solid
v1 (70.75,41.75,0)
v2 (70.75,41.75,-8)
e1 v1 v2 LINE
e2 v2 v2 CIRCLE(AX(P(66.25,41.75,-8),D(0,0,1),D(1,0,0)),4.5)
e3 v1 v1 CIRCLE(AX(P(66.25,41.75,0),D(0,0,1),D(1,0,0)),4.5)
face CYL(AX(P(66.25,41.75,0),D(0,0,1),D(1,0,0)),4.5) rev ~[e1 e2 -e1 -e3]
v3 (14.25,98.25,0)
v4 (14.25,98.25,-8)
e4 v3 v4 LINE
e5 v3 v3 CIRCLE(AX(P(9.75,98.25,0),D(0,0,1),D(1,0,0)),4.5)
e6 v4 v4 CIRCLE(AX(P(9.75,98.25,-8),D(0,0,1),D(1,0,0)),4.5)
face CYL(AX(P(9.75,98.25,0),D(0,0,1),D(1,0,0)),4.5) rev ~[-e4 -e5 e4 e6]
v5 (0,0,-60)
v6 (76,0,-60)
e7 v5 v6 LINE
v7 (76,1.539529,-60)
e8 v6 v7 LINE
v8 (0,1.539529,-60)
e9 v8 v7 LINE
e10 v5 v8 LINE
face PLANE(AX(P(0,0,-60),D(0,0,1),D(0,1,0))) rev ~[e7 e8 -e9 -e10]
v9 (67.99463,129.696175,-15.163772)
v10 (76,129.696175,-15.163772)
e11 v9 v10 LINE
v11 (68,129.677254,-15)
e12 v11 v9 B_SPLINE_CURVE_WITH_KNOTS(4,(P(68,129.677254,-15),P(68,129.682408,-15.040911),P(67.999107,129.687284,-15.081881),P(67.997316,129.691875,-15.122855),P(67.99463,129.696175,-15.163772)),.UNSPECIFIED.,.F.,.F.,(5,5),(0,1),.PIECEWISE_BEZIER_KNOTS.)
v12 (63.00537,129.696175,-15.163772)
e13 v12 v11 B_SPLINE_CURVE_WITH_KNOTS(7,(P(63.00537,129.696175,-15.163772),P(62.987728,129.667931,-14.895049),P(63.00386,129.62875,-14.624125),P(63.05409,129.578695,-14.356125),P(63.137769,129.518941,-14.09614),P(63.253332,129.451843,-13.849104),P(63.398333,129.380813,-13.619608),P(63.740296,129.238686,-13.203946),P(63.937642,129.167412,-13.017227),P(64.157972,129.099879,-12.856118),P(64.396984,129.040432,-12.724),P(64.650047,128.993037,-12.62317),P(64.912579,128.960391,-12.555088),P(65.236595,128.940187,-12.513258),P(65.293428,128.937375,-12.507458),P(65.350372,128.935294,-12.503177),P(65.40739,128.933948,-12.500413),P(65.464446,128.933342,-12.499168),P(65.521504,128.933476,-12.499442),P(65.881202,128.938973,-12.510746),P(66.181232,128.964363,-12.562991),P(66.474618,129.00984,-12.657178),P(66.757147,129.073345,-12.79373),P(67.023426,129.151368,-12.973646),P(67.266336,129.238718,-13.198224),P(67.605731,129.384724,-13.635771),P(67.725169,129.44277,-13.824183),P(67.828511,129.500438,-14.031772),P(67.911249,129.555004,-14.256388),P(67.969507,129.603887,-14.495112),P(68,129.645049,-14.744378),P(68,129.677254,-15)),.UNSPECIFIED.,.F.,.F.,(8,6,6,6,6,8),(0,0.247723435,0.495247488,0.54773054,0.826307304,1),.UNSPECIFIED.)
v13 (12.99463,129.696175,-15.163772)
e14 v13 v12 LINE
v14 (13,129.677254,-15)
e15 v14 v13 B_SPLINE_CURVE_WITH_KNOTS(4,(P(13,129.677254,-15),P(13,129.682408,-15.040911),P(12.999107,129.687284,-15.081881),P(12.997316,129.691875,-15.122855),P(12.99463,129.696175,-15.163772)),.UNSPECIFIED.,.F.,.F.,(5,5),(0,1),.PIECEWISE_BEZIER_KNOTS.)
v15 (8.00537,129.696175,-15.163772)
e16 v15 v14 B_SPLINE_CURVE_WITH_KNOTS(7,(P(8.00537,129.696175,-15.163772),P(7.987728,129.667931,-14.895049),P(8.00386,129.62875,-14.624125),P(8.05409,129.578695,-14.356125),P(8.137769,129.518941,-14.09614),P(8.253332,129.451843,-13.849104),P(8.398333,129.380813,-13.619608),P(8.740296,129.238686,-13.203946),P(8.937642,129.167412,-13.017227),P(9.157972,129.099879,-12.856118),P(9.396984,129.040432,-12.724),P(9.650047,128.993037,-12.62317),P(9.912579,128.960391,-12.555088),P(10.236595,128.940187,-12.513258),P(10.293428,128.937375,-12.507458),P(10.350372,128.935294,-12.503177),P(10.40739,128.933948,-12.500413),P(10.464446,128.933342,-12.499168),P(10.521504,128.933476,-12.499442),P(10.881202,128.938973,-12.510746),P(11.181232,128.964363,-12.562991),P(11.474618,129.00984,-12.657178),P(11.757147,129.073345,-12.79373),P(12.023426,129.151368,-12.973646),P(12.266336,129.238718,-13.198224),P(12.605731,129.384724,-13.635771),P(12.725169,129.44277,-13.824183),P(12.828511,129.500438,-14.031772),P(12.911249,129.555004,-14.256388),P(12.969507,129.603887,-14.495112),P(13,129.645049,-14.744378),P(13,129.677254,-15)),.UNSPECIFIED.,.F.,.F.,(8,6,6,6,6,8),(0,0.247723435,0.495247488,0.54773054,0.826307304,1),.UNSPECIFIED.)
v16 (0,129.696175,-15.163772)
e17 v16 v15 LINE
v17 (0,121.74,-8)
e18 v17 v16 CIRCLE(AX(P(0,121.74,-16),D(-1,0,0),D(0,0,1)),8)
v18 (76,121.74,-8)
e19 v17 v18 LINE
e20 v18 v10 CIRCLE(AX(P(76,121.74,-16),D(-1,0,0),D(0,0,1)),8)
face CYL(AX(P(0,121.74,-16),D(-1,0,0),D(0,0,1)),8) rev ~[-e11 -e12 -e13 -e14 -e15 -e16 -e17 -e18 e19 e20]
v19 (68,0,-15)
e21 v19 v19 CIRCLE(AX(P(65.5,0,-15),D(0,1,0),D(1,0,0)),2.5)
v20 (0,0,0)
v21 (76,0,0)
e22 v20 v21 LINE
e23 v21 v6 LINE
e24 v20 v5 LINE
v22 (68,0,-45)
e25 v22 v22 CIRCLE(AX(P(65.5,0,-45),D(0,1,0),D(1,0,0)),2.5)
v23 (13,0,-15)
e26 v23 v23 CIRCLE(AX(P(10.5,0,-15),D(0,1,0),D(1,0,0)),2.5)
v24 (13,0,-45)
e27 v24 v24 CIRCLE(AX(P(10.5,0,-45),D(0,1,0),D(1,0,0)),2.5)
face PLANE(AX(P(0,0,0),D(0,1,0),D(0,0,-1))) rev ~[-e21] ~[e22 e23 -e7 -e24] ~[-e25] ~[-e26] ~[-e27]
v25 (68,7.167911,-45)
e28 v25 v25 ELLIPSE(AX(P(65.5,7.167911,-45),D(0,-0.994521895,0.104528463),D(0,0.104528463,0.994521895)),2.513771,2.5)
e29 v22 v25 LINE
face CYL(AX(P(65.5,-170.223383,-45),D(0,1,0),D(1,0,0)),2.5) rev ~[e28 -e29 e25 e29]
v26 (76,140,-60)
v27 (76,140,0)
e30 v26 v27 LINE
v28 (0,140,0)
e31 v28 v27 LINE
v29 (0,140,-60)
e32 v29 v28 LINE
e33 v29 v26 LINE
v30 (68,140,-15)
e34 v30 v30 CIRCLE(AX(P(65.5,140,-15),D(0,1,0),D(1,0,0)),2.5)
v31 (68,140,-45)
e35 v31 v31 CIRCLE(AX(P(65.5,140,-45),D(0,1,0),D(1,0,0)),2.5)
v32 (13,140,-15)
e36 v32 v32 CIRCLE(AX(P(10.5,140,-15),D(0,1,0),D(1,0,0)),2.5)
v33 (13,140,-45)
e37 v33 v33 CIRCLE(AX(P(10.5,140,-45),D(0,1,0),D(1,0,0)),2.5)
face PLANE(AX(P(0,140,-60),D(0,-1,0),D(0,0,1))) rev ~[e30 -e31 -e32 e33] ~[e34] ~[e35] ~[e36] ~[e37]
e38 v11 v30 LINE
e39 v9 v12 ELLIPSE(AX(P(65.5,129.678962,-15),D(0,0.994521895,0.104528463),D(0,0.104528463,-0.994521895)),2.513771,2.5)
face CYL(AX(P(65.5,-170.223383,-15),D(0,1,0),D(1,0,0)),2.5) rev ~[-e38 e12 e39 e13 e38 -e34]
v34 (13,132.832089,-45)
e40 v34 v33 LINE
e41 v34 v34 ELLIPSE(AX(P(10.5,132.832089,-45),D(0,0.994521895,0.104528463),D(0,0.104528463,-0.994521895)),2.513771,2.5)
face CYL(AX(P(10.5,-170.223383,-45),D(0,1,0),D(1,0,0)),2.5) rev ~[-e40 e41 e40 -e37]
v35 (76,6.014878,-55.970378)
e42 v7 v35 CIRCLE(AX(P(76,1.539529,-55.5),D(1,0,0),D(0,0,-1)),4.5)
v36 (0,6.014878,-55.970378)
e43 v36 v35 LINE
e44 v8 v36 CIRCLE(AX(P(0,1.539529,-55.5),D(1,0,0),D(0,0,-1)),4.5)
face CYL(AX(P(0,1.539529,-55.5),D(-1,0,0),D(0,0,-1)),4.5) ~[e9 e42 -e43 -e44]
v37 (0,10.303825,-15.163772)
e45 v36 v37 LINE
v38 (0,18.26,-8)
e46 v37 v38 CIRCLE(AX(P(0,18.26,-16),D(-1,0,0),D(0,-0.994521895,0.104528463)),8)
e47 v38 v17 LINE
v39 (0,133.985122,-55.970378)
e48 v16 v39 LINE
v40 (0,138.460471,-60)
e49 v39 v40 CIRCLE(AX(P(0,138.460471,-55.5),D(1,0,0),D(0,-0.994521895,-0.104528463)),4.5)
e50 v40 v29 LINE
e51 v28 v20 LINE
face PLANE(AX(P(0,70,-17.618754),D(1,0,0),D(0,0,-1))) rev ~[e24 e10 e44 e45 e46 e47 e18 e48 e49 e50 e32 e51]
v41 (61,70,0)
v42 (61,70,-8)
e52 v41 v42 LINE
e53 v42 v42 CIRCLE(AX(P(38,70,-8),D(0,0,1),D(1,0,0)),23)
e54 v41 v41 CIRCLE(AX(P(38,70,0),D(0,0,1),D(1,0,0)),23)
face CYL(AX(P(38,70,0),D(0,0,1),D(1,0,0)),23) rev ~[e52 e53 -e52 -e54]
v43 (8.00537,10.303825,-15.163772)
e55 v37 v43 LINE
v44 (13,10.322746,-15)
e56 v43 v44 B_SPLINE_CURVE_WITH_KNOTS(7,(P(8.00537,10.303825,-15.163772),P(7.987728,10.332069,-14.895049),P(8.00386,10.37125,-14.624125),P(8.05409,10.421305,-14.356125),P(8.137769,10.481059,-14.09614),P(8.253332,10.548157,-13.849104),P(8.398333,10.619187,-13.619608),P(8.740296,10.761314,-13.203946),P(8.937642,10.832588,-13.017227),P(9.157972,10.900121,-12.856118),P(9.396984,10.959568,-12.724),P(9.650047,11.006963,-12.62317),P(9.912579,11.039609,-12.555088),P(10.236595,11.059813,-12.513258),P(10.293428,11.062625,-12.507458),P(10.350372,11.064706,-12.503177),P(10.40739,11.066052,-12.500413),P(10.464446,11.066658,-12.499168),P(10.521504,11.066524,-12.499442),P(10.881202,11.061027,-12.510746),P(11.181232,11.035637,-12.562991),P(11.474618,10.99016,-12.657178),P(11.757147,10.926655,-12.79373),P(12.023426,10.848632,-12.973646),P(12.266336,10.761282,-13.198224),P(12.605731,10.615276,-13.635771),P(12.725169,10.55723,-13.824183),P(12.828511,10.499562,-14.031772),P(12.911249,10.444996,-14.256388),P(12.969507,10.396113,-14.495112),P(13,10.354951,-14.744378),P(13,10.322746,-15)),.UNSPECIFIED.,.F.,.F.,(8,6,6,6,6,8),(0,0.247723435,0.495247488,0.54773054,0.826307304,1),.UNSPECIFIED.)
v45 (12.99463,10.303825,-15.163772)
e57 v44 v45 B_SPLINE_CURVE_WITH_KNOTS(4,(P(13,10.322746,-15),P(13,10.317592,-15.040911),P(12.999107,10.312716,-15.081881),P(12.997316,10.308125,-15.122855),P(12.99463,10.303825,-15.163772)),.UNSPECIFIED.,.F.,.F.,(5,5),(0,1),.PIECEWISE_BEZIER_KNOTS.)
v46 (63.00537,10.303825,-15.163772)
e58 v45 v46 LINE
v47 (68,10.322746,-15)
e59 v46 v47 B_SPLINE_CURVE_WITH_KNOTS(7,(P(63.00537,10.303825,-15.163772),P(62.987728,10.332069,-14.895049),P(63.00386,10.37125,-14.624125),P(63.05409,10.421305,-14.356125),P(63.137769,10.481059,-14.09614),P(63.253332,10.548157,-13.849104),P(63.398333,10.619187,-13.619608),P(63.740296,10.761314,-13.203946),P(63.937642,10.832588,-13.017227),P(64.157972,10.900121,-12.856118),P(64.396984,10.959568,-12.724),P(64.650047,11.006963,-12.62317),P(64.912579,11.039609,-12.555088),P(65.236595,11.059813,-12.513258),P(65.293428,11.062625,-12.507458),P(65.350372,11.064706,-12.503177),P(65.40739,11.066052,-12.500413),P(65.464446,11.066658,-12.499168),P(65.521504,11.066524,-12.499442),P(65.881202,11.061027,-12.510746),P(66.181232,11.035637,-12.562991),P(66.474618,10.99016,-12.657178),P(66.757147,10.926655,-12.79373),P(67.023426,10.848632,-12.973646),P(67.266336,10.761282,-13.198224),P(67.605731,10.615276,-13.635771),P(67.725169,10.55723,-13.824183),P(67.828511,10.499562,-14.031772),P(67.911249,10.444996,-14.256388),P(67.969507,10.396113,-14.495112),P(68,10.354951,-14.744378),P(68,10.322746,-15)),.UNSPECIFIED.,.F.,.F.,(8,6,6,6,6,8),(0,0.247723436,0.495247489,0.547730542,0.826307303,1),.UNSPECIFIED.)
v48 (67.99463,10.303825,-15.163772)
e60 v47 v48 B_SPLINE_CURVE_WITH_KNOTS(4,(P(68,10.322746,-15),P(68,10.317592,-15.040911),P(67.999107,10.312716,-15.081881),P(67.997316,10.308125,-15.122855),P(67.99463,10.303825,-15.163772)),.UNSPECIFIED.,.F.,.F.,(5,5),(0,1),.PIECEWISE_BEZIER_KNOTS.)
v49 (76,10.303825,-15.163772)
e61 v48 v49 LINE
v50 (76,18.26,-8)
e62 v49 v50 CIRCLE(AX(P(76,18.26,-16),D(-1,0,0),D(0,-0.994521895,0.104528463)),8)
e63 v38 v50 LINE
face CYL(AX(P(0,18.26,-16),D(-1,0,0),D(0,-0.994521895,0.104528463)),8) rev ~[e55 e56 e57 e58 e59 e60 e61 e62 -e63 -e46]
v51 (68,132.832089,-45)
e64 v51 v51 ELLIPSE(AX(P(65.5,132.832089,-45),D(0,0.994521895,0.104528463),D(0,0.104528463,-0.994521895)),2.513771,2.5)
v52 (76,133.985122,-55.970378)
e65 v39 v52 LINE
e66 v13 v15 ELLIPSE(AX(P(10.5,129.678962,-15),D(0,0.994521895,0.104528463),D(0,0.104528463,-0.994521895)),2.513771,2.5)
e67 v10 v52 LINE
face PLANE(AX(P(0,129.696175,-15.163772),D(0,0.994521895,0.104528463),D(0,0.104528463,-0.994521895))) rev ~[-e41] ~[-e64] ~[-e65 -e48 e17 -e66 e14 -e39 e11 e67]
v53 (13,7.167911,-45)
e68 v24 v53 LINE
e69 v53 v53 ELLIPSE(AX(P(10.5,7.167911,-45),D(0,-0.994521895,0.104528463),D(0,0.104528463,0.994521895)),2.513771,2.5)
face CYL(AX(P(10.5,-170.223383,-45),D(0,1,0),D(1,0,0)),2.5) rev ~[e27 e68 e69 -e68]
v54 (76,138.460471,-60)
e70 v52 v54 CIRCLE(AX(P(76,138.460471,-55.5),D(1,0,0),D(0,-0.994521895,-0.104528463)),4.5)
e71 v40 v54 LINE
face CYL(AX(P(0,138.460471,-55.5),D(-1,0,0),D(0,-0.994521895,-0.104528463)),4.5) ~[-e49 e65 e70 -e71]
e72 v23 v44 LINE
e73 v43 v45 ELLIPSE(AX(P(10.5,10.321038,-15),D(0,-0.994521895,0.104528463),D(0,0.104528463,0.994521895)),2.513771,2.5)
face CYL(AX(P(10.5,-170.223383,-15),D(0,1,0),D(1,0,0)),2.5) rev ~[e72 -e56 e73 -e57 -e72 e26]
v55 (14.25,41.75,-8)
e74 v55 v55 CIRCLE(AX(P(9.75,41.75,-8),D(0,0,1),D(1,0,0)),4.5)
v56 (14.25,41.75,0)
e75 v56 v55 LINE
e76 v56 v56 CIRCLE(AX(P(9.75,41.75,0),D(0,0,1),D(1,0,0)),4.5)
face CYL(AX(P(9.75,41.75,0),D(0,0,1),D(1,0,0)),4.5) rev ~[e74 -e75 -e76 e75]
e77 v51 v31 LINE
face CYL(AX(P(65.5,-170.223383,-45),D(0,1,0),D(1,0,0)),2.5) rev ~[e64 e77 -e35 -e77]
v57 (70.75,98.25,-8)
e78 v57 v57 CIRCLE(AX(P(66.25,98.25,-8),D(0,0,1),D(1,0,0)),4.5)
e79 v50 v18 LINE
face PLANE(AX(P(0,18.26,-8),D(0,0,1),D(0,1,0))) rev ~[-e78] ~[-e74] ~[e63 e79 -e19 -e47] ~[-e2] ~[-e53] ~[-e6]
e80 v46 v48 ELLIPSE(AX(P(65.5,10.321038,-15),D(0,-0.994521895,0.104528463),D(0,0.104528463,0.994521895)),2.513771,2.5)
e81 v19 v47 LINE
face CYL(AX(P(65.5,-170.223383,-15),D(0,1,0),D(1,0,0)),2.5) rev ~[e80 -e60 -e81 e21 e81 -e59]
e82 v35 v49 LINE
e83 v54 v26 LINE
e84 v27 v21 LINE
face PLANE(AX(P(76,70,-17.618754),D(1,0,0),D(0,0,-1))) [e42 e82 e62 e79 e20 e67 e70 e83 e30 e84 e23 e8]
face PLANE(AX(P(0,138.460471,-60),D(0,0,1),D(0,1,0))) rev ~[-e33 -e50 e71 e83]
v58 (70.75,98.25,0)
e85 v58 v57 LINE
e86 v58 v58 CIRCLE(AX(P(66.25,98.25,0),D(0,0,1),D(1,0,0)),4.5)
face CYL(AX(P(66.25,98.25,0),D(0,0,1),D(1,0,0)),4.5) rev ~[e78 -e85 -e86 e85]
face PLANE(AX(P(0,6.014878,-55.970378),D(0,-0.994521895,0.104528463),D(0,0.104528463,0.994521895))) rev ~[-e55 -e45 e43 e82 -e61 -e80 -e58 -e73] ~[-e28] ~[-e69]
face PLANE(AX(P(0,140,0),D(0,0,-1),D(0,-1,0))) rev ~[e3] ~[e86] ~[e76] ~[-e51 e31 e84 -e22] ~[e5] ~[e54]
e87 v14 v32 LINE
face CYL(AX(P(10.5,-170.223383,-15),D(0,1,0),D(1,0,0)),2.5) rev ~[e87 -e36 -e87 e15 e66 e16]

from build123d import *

# Parameters (mm, degrees)
MEMBER_1_DEPTH      = 76
SKETCH_4_R          = 23
CUT_EXTRUDE_1_DEPTH = 171.223382648
SKETCH_6_R          = 4.5
CUT_EXTRUDE_2_DEPTH = 171.223382648
HOLE_WIZARD_M6_1_D  = 5


with BuildPart() as part:
    # Sketch11 → Member 1 (new body)
    with BuildSketch(Plane(origin=(0, 0, 0), x_dir=(0, 0, -1), z_dir=(1, 0, 0))):
        with BuildLine():
            Line((60, 140), (0, 140))
            Line((0, 140), (0, 0))
            Line((0, 0), (60, 0))
            Line((60, 0), (60, 1.539529212))
            ThreePointArc((60, 1.539529212), (58.844151715, 4.550616941), (55.970378085, 6.014877742))
            Line((55.970378085, 6.014877742), (15.163772294, 10.303824837))
            ThreePointArc((15.163772294, 10.303824837), (10.054841396, 12.906955149), (8, 18.26))
            Line((8, 18.26), (8, 121.74))
            ThreePointArc((8, 121.74), (10.054841396, 127.093044851), (15.163772294, 129.696175163))
            Line((15.163772294, 129.696175163), (55.970378085, 133.985122258))
            ThreePointArc((55.970378085, 133.985122258), (58.844151715, 135.449383059), (60, 138.460470788))
            Line((60, 138.460470788), (60, 140))
        make_face()
    extrude(amount=MEMBER_1_DEPTH)

    # 草图4 → 切除-拉伸1 (cut, through all)
    with BuildSketch(Plane.XY):
        with Locations((38, 70)):
            Circle(SKETCH_4_R)
    extrude(amount=-CUT_EXTRUDE_1_DEPTH, mode=Mode.SUBTRACT)

    # 草图6 → 切除-拉伸2 (cut, through all)
    with BuildSketch(Plane.XY):
        with Locations((66.25, 41.75)):
            Circle(SKETCH_6_R)
        with Locations((9.75, 41.75)):
            Circle(SKETCH_6_R)
        with Locations((66.25, 98.25)):
            Circle(SKETCH_6_R)
        with Locations((9.75, 98.25)):
            Circle(SKETCH_6_R)
    extrude(amount=-CUT_EXTRUDE_2_DEPTH, mode=Mode.SUBTRACT)

    # M6 螺纹孔1 (through all)
    with Locations(Plane(origin=(0, 0, 0), x_dir=(-1, 0, 0), z_dir=(0, -1, 0))):
        with Locations((-65.5, 15), (-65.5, 45), (-10.5, 15), (-10.5, 45)):
            Hole(HOLE_WIZARD_M6_1_D / 2)


solid = part.part
